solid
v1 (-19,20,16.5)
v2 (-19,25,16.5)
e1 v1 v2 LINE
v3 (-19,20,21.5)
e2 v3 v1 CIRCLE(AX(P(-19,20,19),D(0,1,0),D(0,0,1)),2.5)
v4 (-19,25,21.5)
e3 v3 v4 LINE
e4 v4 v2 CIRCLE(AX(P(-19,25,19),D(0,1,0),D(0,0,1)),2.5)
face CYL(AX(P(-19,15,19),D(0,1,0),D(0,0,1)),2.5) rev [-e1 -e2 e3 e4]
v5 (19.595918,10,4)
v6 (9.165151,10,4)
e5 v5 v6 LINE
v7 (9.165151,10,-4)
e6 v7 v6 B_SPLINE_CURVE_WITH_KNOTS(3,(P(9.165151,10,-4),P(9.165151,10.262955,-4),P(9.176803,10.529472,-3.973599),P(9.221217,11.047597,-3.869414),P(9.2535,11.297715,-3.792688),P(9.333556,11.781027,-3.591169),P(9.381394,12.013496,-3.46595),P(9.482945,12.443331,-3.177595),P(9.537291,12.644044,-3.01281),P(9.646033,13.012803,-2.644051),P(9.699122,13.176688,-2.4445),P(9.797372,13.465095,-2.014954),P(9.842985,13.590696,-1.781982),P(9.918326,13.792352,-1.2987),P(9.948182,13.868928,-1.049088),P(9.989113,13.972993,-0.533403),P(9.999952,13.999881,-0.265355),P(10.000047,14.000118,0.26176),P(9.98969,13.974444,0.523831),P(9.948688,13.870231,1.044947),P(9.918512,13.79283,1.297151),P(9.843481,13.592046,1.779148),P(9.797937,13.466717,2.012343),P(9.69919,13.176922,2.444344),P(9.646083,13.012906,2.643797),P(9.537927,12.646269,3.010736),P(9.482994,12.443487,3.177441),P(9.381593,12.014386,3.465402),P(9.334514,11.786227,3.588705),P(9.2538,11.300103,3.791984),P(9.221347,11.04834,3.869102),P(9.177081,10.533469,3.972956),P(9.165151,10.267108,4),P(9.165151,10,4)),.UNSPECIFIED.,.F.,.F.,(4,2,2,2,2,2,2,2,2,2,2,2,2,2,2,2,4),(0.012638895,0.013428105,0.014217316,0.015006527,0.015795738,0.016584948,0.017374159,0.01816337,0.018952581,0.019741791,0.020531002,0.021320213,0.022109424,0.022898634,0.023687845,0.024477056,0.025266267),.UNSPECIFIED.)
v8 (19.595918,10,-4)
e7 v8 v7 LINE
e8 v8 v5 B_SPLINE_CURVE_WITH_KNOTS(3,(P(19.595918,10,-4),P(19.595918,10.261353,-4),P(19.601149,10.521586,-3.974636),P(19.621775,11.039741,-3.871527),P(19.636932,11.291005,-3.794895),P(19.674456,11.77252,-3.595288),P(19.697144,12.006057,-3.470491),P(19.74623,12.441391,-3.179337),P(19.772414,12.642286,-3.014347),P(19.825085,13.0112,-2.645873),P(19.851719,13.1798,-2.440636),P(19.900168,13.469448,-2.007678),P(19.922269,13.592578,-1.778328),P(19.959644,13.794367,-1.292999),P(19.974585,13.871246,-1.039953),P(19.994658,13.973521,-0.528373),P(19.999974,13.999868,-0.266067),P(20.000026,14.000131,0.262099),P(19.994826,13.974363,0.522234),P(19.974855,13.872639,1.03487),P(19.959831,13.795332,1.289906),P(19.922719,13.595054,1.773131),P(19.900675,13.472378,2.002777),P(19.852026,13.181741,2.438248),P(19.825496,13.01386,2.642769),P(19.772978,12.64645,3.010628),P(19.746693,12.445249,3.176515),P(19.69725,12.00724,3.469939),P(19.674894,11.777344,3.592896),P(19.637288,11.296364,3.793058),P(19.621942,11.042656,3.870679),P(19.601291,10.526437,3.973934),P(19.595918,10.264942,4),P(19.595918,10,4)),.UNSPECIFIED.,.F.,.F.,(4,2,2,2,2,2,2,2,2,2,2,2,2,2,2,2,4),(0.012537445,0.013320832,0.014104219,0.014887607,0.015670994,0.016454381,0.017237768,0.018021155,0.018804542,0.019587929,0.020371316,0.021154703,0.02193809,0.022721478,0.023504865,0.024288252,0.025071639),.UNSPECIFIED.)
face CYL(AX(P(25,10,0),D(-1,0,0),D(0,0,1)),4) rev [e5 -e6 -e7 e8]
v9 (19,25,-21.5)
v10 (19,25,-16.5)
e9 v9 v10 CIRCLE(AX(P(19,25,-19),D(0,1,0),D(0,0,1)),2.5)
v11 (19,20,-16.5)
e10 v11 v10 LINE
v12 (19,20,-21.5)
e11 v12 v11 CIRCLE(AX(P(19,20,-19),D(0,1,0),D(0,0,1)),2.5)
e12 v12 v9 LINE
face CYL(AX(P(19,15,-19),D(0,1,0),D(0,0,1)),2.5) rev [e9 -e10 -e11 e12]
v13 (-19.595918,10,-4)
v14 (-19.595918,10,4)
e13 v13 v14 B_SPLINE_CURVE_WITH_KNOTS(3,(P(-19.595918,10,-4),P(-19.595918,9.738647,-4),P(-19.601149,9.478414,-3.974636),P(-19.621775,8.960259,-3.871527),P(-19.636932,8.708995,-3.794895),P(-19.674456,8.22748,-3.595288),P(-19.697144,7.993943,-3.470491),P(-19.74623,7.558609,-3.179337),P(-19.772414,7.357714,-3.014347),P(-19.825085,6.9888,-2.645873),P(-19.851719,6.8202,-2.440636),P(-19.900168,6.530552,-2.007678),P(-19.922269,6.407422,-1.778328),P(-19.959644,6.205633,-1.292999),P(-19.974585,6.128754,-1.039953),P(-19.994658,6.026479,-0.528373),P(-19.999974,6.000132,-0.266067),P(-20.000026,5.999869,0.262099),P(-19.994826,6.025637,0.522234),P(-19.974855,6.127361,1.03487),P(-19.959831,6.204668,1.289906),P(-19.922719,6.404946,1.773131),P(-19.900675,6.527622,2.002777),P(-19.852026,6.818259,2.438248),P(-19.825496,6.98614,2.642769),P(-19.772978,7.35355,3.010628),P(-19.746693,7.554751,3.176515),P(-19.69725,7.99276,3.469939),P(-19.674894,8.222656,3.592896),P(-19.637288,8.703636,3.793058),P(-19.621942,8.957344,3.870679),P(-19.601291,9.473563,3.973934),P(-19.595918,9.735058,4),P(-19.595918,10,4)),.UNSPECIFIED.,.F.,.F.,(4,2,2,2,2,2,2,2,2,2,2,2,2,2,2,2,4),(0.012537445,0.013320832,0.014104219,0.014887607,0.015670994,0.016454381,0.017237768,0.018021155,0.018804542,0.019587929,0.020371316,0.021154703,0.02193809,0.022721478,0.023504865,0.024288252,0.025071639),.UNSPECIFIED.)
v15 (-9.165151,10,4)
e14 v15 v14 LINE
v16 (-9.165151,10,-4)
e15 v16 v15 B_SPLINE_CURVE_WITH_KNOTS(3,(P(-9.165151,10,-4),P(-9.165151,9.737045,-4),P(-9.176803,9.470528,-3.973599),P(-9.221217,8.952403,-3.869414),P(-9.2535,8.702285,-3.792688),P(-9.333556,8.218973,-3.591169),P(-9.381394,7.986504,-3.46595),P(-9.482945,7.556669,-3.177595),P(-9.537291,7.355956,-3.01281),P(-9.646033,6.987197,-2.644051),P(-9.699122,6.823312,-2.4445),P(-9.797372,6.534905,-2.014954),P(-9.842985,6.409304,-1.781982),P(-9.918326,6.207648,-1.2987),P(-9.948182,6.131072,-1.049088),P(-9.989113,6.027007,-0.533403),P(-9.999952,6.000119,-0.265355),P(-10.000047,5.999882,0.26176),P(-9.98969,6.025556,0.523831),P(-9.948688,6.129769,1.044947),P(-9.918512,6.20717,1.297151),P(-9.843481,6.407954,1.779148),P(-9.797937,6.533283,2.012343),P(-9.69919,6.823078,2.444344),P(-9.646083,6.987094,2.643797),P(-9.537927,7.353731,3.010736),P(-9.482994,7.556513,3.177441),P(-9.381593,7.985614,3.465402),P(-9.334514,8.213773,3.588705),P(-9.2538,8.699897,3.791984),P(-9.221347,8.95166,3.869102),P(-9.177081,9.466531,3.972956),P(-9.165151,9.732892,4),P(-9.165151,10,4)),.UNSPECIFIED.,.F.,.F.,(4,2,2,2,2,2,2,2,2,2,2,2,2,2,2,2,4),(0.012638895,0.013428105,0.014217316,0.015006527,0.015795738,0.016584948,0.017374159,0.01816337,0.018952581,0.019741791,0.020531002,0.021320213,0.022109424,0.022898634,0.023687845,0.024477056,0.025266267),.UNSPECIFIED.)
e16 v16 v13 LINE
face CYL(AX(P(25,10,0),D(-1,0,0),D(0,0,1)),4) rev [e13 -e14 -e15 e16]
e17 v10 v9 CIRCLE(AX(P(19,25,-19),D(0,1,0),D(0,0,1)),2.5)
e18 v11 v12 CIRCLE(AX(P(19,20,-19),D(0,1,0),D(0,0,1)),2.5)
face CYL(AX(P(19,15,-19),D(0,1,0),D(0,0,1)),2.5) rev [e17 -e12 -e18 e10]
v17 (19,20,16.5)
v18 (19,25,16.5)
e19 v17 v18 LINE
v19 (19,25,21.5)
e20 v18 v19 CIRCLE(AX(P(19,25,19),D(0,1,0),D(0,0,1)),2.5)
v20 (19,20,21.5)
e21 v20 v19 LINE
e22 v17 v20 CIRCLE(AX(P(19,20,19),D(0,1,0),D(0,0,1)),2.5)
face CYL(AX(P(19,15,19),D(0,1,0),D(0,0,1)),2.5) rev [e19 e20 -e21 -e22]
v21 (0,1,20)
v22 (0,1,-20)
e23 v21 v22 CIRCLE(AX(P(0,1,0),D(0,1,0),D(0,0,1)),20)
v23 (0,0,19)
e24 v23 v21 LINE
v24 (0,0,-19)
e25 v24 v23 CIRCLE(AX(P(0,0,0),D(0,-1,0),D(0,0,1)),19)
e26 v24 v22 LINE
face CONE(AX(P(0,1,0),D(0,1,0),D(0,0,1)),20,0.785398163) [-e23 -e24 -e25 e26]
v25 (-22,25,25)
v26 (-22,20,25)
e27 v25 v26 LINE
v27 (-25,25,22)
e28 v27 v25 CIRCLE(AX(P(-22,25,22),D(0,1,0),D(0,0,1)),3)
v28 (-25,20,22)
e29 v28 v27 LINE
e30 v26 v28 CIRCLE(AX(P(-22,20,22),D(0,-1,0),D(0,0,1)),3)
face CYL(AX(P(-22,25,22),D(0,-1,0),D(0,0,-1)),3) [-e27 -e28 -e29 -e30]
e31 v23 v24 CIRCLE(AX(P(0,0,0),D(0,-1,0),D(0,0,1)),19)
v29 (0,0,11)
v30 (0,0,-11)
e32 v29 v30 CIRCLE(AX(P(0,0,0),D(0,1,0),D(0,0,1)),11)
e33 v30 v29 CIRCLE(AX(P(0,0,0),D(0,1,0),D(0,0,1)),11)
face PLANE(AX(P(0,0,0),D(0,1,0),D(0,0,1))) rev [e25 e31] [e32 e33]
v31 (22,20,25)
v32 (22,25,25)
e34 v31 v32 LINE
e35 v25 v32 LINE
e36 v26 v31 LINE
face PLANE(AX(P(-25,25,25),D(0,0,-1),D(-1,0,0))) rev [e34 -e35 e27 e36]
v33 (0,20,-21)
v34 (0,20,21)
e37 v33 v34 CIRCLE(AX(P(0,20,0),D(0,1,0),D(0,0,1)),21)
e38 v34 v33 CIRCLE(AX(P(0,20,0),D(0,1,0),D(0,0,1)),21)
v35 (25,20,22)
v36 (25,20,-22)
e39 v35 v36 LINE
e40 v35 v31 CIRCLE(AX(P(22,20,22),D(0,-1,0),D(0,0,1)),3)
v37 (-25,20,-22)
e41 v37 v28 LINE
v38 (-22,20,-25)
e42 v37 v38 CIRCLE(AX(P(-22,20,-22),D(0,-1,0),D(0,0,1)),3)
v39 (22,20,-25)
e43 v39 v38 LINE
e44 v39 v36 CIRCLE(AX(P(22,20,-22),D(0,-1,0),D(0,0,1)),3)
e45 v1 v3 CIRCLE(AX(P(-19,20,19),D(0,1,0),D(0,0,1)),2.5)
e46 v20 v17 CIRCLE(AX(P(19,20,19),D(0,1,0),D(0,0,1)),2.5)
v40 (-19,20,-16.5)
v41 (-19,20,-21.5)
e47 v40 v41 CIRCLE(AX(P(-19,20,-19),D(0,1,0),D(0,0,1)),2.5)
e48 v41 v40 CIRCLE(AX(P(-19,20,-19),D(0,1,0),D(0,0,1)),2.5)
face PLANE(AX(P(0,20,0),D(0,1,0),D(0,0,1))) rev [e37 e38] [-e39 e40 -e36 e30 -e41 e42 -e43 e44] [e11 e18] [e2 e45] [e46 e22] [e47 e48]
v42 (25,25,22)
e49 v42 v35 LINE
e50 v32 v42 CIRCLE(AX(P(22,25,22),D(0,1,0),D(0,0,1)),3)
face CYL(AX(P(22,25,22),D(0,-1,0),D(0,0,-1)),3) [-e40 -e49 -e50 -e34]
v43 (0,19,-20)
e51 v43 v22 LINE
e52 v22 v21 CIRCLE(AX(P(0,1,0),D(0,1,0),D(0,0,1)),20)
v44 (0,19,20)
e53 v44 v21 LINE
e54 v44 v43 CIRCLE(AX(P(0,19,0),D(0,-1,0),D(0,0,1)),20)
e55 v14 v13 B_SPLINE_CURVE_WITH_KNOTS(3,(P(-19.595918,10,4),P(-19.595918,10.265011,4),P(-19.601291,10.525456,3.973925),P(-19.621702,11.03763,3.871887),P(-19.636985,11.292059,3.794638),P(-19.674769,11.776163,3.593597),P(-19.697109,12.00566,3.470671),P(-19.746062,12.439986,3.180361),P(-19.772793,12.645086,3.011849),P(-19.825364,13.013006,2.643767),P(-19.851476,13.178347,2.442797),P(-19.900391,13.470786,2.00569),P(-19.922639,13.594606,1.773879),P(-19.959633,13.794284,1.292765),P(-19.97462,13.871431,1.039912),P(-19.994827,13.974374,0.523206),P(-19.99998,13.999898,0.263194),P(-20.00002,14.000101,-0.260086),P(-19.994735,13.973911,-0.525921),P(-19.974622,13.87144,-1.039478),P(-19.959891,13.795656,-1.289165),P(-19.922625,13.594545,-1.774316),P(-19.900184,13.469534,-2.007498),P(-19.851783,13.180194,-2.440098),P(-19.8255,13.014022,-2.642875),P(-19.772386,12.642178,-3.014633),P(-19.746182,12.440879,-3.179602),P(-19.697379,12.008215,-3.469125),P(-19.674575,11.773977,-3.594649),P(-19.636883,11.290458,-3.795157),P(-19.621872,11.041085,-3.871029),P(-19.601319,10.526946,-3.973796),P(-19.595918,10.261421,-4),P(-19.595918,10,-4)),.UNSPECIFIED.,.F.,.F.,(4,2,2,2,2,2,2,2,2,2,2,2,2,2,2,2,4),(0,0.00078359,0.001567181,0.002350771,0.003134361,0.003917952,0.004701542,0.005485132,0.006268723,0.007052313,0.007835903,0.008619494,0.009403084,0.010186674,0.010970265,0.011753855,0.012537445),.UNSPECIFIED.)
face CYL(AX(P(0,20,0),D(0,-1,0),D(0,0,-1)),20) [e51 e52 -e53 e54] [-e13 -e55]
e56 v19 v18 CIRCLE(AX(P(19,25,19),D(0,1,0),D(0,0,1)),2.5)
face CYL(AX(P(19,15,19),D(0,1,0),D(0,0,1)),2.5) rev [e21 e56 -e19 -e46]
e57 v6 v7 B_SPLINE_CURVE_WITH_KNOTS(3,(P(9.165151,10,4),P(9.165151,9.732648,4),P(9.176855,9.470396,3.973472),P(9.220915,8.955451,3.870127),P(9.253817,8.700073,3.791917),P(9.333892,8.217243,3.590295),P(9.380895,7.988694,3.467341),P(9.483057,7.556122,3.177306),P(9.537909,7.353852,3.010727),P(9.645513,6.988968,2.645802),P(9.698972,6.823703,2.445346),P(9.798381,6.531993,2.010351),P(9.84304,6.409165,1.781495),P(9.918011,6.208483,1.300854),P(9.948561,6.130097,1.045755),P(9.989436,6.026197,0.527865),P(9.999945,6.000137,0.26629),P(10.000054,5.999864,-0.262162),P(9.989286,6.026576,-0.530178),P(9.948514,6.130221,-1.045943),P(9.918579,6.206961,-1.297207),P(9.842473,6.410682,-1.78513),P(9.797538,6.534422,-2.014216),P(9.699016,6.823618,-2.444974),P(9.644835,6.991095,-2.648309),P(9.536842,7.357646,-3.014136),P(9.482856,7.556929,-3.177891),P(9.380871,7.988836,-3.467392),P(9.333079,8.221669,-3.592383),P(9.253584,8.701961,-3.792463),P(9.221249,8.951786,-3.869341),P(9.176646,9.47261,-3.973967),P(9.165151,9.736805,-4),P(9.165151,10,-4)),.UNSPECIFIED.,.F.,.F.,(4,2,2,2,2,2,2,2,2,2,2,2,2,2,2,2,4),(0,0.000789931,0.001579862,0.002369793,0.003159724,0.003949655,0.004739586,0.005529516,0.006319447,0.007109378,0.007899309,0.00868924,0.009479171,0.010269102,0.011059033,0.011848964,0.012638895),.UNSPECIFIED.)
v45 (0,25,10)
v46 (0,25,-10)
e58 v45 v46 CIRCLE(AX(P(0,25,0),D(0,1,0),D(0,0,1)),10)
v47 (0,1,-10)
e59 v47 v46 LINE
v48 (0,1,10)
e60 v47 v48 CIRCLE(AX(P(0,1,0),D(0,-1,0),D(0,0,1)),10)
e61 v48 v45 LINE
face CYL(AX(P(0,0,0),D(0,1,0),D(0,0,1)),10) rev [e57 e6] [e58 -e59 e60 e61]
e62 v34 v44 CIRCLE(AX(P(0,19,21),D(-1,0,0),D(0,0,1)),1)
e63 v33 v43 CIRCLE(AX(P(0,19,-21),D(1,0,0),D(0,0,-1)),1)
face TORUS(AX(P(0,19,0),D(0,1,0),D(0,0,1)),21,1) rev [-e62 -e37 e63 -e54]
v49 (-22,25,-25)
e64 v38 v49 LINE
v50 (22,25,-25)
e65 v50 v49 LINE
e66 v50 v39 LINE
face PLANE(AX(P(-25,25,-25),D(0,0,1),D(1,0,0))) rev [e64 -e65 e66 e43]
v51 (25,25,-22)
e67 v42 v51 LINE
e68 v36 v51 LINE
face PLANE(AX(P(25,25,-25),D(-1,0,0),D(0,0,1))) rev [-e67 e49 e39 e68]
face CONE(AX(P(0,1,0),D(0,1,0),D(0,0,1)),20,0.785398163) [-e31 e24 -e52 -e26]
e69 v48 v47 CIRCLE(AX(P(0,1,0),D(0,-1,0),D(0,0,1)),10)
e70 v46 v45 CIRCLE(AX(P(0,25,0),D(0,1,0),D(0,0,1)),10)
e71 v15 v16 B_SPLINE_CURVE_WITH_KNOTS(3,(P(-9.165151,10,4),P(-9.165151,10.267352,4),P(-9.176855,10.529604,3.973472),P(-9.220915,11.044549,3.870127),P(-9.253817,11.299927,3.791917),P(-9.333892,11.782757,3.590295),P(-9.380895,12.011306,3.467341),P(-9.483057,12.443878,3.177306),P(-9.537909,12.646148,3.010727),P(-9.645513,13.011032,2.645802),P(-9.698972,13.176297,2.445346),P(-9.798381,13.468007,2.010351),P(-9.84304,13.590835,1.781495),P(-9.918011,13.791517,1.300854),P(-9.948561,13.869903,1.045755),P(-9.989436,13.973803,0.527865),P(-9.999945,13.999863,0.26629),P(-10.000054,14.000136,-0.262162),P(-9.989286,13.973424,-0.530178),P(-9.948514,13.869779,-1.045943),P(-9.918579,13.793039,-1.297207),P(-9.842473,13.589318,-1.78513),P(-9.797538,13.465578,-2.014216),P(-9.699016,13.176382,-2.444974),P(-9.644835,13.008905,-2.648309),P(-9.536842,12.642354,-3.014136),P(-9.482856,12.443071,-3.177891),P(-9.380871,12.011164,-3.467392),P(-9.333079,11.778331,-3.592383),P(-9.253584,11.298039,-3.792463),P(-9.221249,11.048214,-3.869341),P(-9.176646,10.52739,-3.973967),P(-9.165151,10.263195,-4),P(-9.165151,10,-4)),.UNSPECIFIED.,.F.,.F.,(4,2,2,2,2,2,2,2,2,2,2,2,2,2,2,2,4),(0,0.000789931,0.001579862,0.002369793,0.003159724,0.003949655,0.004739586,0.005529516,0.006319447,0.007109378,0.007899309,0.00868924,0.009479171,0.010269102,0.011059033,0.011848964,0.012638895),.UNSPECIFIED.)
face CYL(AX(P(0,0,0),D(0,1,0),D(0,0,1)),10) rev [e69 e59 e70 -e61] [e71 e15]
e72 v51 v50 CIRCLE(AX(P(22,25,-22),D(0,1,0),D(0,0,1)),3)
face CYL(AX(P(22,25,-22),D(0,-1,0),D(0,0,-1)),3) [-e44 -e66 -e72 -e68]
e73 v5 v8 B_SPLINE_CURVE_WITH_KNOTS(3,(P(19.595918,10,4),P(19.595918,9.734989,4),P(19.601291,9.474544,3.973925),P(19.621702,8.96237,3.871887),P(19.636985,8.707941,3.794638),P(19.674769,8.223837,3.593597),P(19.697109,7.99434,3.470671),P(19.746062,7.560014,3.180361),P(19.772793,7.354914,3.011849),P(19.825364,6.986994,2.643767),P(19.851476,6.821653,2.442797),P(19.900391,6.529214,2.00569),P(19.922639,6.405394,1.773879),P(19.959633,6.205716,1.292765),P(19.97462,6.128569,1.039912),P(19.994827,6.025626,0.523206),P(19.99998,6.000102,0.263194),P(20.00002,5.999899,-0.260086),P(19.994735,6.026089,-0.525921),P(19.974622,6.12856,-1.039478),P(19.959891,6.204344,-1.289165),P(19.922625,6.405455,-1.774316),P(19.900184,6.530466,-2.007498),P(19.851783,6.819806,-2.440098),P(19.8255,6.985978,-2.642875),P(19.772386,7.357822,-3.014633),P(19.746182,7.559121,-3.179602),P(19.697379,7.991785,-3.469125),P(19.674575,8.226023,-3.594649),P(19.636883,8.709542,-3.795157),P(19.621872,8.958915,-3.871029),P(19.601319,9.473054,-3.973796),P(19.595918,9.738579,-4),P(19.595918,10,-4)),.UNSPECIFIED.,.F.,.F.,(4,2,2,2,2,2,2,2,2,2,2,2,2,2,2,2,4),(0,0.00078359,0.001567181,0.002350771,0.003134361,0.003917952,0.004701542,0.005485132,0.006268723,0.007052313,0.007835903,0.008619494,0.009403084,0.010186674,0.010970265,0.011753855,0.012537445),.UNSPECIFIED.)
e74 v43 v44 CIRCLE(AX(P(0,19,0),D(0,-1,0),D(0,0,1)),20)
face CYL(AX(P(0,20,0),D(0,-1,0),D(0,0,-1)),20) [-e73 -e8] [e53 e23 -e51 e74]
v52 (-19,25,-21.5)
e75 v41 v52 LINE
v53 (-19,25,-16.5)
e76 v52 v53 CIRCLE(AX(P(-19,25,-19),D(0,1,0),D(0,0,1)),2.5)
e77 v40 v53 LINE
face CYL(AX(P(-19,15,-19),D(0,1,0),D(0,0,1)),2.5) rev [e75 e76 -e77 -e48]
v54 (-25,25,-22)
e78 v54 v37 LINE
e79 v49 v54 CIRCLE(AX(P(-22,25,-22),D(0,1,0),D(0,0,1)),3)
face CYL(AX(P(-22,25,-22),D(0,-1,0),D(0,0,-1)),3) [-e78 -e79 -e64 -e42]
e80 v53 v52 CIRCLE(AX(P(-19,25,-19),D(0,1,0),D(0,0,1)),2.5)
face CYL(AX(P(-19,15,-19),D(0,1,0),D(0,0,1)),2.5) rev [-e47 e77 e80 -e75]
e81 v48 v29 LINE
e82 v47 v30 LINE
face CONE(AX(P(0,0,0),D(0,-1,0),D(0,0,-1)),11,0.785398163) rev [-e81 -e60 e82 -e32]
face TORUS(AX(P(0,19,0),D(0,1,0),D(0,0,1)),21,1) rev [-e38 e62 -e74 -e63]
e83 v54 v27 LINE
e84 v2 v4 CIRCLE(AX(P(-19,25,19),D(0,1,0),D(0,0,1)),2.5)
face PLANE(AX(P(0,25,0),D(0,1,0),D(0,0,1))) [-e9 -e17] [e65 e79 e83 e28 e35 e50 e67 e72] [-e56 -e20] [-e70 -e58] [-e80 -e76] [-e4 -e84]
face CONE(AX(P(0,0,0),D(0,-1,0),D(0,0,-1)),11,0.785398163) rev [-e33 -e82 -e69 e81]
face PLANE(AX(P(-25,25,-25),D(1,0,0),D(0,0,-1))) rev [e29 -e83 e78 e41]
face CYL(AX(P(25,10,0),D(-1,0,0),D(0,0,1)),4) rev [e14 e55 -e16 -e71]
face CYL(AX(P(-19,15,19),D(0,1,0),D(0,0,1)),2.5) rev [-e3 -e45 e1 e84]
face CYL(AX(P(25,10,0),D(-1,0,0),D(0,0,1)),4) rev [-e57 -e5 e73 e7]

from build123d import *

# Parameters (mm, degrees)
SKETCH1_R               = 20
BOSS_EXTRUDE1_DEPTH     = 20
CUT_EXTRUDE5_DEPTH      = 25
CUT_EXTRUDE5_DEPTH_BACK = 25
SKETCH8_R               = 4
SKETCH9_W               = 50
SKETCH9_H               = 50
BOSS_EXTRUDE3_DEPTH     = 5
SKETCH10_R              = 10
CUT_EXTRUDE6_DEPTH      = 25
SKETCH11_R              = 2.5
CUT_EXTRUDE7_DEPTH      = 10
FILLET1_R               = 3
FILLET2_R               = 1
CHAMFER1_SIZE           = 1


with BuildPart() as part:
    # Sketch1 → Boss-Extrude1 (new body)
    with BuildSketch(Plane(origin=(0, 0, 0), x_dir=(1, 0, 0), z_dir=(0, 1, 0))):
        with Locations(Location((0, 0, 0), (0, 0, 270))):
            Circle(SKETCH1_R)
    extrude(amount=BOSS_EXTRUDE1_DEPTH)

    # Sketch8 → Cut-Extrude5 (cut, two sides: drawn at the far end of the back side and taken through both)
    with BuildSketch(Plane(origin=(0, 0, 0), x_dir=(0, 0, -1), z_dir=(1, 0, 0)).offset(-CUT_EXTRUDE5_DEPTH_BACK)):
        with Locations(Location((0, 10, 0), (0, 0, 180))):
            Circle(SKETCH8_R)
    extrude(amount=CUT_EXTRUDE5_DEPTH + CUT_EXTRUDE5_DEPTH_BACK, mode=Mode.SUBTRACT)

    # Sketch9 → Boss-Extrude3 (add)
    with BuildSketch(Plane(origin=(0, 20, 0), x_dir=(1, 0, 0), z_dir=(0, 1, 0))):
        Rectangle(SKETCH9_W, SKETCH9_H)
    extrude(amount=BOSS_EXTRUDE3_DEPTH)

    # Sketch10 → Cut-Extrude6 (cut)
    with BuildSketch(Plane(origin=(0, 25, 0), x_dir=(1, 0, 0), z_dir=(0, 1, 0))):
        with Locations(Location((0, 0, 0), (0, 0, 270))):
            Circle(SKETCH10_R)
    extrude(amount=-CUT_EXTRUDE6_DEPTH, mode=Mode.SUBTRACT)

    # Sketch11 → Cut-Extrude7 (cut)
    with BuildSketch(Plane(origin=(0, 25, 0), x_dir=(1, 0, 0), z_dir=(0, 1, 0))):
        with Locations(Location((-19, 19, 0), (0, 0, 270))):
            Circle(SKETCH11_R)
        with Locations(Location((-19, -19, 0), (0, 0, 270))):
            Circle(SKETCH11_R)
        with Locations(Location((19, -19, 0), (0, 0, 270))):
            Circle(SKETCH11_R)
        with Locations(Location((19, 19, 0), (0, 0, 270))):
            Circle(SKETCH11_R)
    extrude(amount=-CUT_EXTRUDE7_DEPTH, mode=Mode.SUBTRACT)

    # Fillet1
    fillet1_edges = [part.edges().sort_by_distance(p)[0] for p in [
        (25, 22.5, 25),
        (25, 22.5, -25),
        (-25, 22.5, -25),
        (-25, 22.5, 25),
    ]]
    fillet(fillet1_edges, radius=FILLET1_R)

    # Fillet2
    fillet2_edges = [part.edges().sort_by_distance(p)[0] for p in [
        (0, 20, -20),
    ]]
    fillet(fillet2_edges, radius=FILLET2_R)

    # Chamfer1
    chamfer1_edges = [part.edges().sort_by_distance(p)[0] for p in [
        (0, 0, -20),
        (0, 0, -10),
    ]]
    chamfer(chamfer1_edges, length=CHAMFER1_SIZE)


solid = part.part
